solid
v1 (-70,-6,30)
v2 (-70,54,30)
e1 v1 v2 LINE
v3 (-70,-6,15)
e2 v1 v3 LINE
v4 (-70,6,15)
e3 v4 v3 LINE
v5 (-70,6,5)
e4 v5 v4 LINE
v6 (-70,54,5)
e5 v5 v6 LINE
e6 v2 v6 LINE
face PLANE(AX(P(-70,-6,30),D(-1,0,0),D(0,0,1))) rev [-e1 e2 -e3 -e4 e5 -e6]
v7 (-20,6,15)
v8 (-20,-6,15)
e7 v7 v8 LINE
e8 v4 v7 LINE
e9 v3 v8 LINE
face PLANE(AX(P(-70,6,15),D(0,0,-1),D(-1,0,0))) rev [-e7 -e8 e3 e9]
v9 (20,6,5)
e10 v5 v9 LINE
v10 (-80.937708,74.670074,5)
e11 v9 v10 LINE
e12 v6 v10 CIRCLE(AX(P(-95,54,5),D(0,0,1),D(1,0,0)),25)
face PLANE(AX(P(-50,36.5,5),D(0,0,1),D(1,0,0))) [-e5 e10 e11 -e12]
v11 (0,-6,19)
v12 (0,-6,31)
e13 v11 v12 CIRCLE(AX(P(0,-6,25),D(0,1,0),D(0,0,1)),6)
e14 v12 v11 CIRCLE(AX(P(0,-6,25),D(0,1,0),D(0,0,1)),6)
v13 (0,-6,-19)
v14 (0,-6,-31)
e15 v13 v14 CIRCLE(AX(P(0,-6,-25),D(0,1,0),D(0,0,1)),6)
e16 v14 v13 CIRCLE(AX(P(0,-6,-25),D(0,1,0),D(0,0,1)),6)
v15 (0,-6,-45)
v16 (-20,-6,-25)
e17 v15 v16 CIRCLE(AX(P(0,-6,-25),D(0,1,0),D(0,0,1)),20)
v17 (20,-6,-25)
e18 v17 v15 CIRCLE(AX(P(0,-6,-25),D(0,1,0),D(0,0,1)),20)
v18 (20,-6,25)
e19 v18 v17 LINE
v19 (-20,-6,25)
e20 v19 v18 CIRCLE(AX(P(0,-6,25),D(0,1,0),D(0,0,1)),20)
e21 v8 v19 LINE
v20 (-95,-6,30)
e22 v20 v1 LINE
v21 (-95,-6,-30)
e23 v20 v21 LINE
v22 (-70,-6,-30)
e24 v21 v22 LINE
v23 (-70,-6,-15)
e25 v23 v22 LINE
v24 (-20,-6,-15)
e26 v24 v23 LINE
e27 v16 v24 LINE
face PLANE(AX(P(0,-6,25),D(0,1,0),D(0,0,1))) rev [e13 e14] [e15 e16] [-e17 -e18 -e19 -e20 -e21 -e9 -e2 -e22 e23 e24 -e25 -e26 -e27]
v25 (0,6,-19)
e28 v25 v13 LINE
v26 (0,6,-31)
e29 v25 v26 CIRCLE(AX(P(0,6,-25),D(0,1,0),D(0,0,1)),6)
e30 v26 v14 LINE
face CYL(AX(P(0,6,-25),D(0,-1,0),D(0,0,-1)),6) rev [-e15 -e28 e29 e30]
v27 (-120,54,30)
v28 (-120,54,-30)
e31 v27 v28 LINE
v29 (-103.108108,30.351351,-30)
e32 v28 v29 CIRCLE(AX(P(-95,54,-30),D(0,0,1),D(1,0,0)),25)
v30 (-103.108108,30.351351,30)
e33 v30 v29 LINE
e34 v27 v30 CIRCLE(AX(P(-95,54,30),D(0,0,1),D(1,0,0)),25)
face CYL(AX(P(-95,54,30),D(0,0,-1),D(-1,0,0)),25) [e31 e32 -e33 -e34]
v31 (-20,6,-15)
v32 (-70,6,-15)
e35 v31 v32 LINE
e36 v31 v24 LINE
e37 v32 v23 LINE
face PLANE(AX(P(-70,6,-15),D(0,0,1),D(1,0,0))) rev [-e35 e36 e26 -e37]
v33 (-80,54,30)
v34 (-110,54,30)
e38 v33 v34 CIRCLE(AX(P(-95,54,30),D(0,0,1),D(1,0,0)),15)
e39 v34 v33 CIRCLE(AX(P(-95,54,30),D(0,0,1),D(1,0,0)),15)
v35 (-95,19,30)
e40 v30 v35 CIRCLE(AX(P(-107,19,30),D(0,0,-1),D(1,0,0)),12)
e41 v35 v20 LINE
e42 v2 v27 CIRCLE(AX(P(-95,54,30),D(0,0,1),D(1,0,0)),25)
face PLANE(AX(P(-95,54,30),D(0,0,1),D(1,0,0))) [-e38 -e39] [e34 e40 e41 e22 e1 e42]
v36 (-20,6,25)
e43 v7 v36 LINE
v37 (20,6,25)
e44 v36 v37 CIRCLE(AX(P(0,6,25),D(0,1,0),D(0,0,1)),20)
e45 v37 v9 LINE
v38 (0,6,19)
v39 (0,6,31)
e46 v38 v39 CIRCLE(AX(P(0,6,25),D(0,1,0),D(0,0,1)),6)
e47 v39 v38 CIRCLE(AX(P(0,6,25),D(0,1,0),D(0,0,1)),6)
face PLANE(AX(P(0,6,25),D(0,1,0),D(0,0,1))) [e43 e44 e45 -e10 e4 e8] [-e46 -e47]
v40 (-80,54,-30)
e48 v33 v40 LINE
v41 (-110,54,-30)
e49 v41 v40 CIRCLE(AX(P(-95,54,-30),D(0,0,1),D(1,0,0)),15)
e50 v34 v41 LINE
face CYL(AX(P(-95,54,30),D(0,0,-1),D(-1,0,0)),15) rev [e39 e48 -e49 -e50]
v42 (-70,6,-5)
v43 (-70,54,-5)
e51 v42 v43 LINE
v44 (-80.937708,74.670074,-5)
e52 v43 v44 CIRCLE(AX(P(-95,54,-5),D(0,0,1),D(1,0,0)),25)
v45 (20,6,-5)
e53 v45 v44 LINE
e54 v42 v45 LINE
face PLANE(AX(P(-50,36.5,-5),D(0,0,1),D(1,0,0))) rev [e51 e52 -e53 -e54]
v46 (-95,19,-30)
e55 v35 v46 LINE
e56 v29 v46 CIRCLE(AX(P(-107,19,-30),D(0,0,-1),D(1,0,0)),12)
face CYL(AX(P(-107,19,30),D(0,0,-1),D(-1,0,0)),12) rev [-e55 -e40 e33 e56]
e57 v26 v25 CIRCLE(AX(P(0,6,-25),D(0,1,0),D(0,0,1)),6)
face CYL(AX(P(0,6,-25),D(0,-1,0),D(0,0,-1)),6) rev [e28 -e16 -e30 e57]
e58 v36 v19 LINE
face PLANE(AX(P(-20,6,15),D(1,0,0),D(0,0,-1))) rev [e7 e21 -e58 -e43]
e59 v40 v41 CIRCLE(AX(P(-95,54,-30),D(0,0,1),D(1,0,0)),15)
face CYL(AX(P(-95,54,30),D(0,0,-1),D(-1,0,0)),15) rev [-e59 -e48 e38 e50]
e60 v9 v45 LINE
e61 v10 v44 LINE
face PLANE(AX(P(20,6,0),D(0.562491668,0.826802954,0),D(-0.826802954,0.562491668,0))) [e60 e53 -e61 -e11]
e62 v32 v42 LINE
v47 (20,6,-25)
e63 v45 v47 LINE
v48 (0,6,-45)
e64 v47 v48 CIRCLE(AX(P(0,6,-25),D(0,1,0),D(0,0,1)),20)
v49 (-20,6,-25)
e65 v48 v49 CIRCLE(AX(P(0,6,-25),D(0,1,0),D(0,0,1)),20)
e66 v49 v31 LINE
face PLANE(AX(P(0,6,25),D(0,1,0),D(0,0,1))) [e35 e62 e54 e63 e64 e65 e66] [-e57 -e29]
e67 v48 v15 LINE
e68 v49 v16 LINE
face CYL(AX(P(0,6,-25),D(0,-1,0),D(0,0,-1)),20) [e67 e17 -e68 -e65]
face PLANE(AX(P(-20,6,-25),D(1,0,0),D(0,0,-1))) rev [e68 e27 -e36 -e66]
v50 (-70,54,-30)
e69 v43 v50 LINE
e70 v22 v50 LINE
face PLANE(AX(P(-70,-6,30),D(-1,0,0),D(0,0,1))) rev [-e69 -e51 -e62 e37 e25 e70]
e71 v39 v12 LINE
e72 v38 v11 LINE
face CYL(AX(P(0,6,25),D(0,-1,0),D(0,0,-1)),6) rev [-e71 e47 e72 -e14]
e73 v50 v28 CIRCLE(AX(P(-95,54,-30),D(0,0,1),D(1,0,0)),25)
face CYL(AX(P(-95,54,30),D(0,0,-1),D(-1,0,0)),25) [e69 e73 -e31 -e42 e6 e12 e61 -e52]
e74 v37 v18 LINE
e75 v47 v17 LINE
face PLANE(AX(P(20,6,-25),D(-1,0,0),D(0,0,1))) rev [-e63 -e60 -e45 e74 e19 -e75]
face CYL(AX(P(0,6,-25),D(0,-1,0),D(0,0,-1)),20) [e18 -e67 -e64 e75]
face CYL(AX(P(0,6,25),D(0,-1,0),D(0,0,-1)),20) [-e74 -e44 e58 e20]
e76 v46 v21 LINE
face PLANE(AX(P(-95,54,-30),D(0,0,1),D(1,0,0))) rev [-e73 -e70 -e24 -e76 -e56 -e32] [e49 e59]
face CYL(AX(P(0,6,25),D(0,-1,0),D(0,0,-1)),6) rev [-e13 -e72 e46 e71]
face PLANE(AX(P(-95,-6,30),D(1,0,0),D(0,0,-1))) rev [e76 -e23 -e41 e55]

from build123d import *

# Parameters (mm, degrees)
BASE_PLATE_SKETCH_R       = 6
BASE_PLATE_DEPTH          = 6
BEARING_UPRIGHT_SKETCH_R  = 15
BEARING_UPRIGHT_DEPTH     = 30
SUPPORT_RIB_10MM_REACH    = 152.552
SUPPORT_RIB_SKETCH_WALL_W = 425.186572672
SUPPORT_RIB_SKETCH_WALL_H = 10


with BuildPart() as part:
    # Base Plate Sketch → Base Plate (new, symmetric)
    with BuildSketch(Plane(origin=(0, 0, 0), x_dir=(1, 0, 0), z_dir=(0, 1, 0))):
        with BuildLine():
            Line((20, 25), (20, -25))
            ThreePointArc((20, -25), (0, -45), (-20, -25))
            Line((-20, -25), (-20, -15))
            Line((-20, -15), (-70, -15))
            Line((-70, -15), (-70, 15))
            Line((-70, 15), (-20, 15))
            Line((-20, 15), (-20, 25))
            ThreePointArc((-20, 25), (0, 45), (20, 25))
        make_face()
        with Locations(Location((0, 25, 0), (0, 0, 270))):
            Circle(BASE_PLATE_SKETCH_R, mode=Mode.SUBTRACT)
        with Locations(Location((0, -25, 0), (0, 0, 270))):
            Circle(BASE_PLATE_SKETCH_R, mode=Mode.SUBTRACT)
    extrude(amount=BASE_PLATE_DEPTH, both=True)

    # Bearing Upright Sketch → Bearing Upright (add, symmetric)
    with BuildSketch(Plane.XY):
        with BuildLine():
            Line((-70, -6), (-95, -6))
            Line((-95, -6), (-95, 19))
            ThreePointArc((-95, 19), (-97.235198346, 25.974858325), (-103.108108108, 30.351351351))
            ThreePointArc((-103.108108108, 30.351351351), (-109.530954843, 74.34333678), (-70, 54))
            Line((-70, 54), (-70, -6))
        make_face()
        with Locations((-95, 54)):
            Circle(BEARING_UPRIGHT_SKETCH_R, mode=Mode.SUBTRACT)
    extrude(amount=BEARING_UPRIGHT_DEPTH, both=True)

    # Support Rib Sketch wall → Support Rib 10mm (add, up to next)
    with BuildSketch(Plane(origin=(-30.468854155, 40.335036919, 0), x_dir=(-0.826802953509, 0.562491667554, 0), z_dir=(-0.562491667554, -0.826802953509, 0)), mode=Mode.PRIVATE) as support_rib_10mm_sk1:
        Rectangle(SUPPORT_RIB_SKETCH_WALL_W, SUPPORT_RIB_SKETCH_WALL_H)
    support_rib_10mm_tool1 = extrude(support_rib_10mm_sk1.sketch, amount=SUPPORT_RIB_10MM_REACH, mode=Mode.PRIVATE) - part.part
    add(support_rib_10mm_tool1.solids().sort_by_distance((-30.468854155, 40.335036919, 0))[0])


solid = part.part
